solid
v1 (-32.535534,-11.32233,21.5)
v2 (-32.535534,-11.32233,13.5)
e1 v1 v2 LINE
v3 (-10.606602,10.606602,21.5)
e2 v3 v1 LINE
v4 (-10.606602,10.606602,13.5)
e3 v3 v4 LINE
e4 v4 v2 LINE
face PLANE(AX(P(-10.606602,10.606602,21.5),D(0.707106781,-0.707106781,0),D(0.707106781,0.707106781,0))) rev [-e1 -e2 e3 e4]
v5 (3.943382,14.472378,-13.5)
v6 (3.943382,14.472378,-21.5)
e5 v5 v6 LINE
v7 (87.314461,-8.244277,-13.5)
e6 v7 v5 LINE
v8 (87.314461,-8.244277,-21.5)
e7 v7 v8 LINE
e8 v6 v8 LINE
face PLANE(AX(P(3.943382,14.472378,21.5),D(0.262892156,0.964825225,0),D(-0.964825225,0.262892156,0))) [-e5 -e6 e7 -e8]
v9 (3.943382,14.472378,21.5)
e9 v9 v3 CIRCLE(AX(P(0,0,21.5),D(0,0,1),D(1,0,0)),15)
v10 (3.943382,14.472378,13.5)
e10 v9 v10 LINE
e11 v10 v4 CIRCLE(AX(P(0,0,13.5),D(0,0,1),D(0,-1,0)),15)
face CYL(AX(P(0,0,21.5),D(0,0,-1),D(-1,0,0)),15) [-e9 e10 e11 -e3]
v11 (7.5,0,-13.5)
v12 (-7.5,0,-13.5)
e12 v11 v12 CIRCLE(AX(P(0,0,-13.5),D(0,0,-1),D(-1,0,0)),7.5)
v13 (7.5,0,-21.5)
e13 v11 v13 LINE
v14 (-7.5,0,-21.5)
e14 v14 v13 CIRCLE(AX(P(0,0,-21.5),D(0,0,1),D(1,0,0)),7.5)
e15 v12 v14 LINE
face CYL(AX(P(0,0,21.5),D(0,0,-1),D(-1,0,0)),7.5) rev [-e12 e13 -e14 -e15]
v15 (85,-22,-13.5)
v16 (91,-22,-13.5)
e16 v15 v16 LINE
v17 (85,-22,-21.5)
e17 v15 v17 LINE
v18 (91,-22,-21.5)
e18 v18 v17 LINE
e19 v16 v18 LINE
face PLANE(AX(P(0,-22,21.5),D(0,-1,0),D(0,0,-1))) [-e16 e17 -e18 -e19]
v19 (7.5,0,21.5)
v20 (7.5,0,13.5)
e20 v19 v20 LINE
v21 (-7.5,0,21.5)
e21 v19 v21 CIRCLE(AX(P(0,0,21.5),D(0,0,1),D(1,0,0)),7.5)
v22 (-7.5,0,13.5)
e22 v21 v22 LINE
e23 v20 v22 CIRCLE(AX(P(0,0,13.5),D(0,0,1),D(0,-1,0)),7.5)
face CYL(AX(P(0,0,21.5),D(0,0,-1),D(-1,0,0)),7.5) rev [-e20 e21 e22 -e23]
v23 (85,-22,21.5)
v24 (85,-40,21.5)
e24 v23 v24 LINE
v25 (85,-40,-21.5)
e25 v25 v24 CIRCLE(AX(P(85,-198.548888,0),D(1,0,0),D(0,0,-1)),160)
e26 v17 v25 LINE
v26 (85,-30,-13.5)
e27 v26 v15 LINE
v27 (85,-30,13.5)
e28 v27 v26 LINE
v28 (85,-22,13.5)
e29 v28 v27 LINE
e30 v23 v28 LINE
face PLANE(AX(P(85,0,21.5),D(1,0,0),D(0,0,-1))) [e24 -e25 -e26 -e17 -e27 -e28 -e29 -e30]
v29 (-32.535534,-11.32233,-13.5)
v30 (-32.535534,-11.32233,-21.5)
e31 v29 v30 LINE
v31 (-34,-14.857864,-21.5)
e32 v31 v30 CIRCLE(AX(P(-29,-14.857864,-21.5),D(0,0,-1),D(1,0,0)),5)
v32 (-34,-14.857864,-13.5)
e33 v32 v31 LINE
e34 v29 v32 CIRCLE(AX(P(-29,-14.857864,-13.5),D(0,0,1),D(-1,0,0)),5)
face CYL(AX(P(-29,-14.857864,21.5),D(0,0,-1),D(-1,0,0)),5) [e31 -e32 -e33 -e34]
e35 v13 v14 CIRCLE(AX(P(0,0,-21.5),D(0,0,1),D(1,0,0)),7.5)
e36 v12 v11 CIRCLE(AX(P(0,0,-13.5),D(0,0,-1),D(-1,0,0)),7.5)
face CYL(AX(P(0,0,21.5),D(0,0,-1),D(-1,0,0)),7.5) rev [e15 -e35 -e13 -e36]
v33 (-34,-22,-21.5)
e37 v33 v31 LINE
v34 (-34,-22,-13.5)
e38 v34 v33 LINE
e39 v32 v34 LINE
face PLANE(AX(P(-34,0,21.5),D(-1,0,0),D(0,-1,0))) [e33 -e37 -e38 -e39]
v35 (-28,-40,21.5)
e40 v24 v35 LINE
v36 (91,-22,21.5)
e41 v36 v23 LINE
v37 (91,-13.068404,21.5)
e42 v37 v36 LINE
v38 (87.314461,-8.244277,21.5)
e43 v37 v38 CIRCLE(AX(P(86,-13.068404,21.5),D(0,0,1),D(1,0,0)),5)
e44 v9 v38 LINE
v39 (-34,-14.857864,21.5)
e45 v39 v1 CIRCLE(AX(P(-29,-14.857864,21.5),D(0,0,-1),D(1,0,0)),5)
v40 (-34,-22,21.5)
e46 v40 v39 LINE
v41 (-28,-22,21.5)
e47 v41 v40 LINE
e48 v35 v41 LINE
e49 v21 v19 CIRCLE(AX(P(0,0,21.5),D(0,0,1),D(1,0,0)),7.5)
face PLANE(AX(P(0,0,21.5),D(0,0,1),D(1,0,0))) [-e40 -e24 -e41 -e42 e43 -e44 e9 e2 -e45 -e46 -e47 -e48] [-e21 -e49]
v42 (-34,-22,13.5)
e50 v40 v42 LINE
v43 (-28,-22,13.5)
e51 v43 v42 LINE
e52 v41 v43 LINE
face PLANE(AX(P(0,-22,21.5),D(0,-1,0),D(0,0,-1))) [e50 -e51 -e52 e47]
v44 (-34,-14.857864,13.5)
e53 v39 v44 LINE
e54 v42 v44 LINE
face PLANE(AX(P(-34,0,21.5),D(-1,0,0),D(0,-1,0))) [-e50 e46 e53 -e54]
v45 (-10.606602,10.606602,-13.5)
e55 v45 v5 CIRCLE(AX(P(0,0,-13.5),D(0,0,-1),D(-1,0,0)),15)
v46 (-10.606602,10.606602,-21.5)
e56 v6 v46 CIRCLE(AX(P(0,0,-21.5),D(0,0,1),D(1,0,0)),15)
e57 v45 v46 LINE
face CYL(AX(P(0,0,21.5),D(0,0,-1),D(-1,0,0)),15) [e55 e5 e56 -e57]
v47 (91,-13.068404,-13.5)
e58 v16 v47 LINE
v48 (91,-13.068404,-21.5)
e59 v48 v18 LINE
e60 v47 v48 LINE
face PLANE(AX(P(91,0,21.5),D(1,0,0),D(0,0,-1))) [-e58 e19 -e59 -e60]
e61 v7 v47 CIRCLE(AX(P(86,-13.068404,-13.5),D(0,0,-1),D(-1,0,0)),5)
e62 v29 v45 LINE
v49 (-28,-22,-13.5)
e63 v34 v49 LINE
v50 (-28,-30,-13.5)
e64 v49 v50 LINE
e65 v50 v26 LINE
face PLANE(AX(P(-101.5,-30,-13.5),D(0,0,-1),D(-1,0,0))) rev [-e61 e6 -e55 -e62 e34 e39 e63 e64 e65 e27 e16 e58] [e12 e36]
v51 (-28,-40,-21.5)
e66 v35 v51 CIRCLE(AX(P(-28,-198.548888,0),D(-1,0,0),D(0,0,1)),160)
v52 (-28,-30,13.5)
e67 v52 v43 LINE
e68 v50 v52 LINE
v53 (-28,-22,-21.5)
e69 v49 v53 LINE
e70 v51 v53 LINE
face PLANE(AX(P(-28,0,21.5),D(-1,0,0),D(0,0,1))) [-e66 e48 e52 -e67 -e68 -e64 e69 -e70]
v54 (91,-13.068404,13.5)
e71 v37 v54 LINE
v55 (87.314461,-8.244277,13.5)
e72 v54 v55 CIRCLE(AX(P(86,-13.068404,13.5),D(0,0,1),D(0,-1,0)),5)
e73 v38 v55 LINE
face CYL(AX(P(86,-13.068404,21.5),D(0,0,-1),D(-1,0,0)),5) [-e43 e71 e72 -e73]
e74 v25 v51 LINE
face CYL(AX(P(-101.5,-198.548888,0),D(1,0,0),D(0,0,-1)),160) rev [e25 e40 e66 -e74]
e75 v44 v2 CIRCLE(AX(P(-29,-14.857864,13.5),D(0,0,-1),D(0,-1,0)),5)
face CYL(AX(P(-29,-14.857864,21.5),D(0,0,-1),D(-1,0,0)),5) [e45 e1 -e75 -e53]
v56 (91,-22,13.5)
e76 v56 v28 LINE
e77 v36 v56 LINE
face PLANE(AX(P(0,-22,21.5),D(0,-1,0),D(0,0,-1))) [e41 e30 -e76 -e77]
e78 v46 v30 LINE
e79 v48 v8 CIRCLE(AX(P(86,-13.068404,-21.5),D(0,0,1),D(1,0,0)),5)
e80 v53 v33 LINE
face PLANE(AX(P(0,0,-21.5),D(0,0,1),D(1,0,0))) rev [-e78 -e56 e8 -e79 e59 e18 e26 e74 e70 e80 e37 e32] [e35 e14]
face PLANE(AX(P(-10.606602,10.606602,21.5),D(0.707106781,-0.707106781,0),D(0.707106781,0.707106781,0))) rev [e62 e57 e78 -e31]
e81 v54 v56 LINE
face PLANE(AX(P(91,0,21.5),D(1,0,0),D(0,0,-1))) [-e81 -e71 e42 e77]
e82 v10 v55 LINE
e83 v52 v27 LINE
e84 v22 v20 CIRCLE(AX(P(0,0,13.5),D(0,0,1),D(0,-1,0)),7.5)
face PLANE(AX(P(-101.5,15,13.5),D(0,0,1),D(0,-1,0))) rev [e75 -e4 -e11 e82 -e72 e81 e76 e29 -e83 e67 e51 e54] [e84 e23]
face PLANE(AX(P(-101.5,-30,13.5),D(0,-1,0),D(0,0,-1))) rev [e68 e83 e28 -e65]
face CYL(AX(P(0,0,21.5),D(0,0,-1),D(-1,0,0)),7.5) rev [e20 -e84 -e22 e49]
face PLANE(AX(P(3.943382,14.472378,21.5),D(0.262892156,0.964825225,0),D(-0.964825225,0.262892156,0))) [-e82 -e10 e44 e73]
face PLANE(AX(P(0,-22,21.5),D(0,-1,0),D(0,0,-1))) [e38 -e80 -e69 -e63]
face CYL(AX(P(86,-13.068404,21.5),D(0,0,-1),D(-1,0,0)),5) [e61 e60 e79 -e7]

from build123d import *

# Parameters (mm, degrees)
CLEVIS_PROFILE_SKETCH_R = 7.5
CLEVIS_BODY_DEPTH       = 21.5
CLEVIS_GAP_SKETCH_W     = 27
CLEVIS_GAP_SKETCH_H     = 45
CLEVIS_GAP_CUT_DEPTH    = 186.5


with BuildPart() as part:
    # Clevis Profile Sketch → Clevis Body (new, symmetric)
    with BuildSketch(Plane.XY):
        with BuildLine():
            ThreePointArc((-34, -14.857864376), (-33.619397663, -12.944447214), (-32.535533906, -11.32233047))
            Line((-32.535533906, -11.32233047), (-10.606601718, 10.606601718))
            ThreePointArc((-10.606601718, 10.606601718), (-3.851711358, 14.497045203), (3.943382345, 14.47237837))
            Line((3.943382345, 14.47237837), (87.314460782, -8.24427748))
            ThreePointArc((87.314460782, -8.24427748), (89.973179074, -10.032971502), (91, -13.068403604))
            Line((91, -13.068403604), (91, -22))
            Line((91, -22), (85, -22))
            Line((85, -22), (85, -40))
            Line((85, -40), (-28, -40))
            Line((-28, -40), (-28, -22))
            Line((-28, -22), (-34, -22))
            Line((-34, -22), (-34, -14.857864376))
        make_face()
        Circle(CLEVIS_PROFILE_SKETCH_R, mode=Mode.SUBTRACT)
    extrude(amount=CLEVIS_BODY_DEPTH, both=True)

    # Clevis Gap Sketch → Clevis Gap Cut (cut, symmetric)
    with BuildSketch(Plane(origin=(85, 0, 0), x_dir=(0, 0, -1), z_dir=(1, 0, 0))):
        with Locations((0, -7.5)):
            Rectangle(CLEVIS_GAP_SKETCH_W, CLEVIS_GAP_SKETCH_H)
        with BuildLine():
            Line((-21.5, -40), (21.5, -40))
            ThreePointArc((21.5, -40), (0, -38.548888359), (-21.5, -40))
        make_face()
    extrude(amount=CLEVIS_GAP_CUT_DEPTH, both=True, mode=Mode.SUBTRACT)


solid = part.part
